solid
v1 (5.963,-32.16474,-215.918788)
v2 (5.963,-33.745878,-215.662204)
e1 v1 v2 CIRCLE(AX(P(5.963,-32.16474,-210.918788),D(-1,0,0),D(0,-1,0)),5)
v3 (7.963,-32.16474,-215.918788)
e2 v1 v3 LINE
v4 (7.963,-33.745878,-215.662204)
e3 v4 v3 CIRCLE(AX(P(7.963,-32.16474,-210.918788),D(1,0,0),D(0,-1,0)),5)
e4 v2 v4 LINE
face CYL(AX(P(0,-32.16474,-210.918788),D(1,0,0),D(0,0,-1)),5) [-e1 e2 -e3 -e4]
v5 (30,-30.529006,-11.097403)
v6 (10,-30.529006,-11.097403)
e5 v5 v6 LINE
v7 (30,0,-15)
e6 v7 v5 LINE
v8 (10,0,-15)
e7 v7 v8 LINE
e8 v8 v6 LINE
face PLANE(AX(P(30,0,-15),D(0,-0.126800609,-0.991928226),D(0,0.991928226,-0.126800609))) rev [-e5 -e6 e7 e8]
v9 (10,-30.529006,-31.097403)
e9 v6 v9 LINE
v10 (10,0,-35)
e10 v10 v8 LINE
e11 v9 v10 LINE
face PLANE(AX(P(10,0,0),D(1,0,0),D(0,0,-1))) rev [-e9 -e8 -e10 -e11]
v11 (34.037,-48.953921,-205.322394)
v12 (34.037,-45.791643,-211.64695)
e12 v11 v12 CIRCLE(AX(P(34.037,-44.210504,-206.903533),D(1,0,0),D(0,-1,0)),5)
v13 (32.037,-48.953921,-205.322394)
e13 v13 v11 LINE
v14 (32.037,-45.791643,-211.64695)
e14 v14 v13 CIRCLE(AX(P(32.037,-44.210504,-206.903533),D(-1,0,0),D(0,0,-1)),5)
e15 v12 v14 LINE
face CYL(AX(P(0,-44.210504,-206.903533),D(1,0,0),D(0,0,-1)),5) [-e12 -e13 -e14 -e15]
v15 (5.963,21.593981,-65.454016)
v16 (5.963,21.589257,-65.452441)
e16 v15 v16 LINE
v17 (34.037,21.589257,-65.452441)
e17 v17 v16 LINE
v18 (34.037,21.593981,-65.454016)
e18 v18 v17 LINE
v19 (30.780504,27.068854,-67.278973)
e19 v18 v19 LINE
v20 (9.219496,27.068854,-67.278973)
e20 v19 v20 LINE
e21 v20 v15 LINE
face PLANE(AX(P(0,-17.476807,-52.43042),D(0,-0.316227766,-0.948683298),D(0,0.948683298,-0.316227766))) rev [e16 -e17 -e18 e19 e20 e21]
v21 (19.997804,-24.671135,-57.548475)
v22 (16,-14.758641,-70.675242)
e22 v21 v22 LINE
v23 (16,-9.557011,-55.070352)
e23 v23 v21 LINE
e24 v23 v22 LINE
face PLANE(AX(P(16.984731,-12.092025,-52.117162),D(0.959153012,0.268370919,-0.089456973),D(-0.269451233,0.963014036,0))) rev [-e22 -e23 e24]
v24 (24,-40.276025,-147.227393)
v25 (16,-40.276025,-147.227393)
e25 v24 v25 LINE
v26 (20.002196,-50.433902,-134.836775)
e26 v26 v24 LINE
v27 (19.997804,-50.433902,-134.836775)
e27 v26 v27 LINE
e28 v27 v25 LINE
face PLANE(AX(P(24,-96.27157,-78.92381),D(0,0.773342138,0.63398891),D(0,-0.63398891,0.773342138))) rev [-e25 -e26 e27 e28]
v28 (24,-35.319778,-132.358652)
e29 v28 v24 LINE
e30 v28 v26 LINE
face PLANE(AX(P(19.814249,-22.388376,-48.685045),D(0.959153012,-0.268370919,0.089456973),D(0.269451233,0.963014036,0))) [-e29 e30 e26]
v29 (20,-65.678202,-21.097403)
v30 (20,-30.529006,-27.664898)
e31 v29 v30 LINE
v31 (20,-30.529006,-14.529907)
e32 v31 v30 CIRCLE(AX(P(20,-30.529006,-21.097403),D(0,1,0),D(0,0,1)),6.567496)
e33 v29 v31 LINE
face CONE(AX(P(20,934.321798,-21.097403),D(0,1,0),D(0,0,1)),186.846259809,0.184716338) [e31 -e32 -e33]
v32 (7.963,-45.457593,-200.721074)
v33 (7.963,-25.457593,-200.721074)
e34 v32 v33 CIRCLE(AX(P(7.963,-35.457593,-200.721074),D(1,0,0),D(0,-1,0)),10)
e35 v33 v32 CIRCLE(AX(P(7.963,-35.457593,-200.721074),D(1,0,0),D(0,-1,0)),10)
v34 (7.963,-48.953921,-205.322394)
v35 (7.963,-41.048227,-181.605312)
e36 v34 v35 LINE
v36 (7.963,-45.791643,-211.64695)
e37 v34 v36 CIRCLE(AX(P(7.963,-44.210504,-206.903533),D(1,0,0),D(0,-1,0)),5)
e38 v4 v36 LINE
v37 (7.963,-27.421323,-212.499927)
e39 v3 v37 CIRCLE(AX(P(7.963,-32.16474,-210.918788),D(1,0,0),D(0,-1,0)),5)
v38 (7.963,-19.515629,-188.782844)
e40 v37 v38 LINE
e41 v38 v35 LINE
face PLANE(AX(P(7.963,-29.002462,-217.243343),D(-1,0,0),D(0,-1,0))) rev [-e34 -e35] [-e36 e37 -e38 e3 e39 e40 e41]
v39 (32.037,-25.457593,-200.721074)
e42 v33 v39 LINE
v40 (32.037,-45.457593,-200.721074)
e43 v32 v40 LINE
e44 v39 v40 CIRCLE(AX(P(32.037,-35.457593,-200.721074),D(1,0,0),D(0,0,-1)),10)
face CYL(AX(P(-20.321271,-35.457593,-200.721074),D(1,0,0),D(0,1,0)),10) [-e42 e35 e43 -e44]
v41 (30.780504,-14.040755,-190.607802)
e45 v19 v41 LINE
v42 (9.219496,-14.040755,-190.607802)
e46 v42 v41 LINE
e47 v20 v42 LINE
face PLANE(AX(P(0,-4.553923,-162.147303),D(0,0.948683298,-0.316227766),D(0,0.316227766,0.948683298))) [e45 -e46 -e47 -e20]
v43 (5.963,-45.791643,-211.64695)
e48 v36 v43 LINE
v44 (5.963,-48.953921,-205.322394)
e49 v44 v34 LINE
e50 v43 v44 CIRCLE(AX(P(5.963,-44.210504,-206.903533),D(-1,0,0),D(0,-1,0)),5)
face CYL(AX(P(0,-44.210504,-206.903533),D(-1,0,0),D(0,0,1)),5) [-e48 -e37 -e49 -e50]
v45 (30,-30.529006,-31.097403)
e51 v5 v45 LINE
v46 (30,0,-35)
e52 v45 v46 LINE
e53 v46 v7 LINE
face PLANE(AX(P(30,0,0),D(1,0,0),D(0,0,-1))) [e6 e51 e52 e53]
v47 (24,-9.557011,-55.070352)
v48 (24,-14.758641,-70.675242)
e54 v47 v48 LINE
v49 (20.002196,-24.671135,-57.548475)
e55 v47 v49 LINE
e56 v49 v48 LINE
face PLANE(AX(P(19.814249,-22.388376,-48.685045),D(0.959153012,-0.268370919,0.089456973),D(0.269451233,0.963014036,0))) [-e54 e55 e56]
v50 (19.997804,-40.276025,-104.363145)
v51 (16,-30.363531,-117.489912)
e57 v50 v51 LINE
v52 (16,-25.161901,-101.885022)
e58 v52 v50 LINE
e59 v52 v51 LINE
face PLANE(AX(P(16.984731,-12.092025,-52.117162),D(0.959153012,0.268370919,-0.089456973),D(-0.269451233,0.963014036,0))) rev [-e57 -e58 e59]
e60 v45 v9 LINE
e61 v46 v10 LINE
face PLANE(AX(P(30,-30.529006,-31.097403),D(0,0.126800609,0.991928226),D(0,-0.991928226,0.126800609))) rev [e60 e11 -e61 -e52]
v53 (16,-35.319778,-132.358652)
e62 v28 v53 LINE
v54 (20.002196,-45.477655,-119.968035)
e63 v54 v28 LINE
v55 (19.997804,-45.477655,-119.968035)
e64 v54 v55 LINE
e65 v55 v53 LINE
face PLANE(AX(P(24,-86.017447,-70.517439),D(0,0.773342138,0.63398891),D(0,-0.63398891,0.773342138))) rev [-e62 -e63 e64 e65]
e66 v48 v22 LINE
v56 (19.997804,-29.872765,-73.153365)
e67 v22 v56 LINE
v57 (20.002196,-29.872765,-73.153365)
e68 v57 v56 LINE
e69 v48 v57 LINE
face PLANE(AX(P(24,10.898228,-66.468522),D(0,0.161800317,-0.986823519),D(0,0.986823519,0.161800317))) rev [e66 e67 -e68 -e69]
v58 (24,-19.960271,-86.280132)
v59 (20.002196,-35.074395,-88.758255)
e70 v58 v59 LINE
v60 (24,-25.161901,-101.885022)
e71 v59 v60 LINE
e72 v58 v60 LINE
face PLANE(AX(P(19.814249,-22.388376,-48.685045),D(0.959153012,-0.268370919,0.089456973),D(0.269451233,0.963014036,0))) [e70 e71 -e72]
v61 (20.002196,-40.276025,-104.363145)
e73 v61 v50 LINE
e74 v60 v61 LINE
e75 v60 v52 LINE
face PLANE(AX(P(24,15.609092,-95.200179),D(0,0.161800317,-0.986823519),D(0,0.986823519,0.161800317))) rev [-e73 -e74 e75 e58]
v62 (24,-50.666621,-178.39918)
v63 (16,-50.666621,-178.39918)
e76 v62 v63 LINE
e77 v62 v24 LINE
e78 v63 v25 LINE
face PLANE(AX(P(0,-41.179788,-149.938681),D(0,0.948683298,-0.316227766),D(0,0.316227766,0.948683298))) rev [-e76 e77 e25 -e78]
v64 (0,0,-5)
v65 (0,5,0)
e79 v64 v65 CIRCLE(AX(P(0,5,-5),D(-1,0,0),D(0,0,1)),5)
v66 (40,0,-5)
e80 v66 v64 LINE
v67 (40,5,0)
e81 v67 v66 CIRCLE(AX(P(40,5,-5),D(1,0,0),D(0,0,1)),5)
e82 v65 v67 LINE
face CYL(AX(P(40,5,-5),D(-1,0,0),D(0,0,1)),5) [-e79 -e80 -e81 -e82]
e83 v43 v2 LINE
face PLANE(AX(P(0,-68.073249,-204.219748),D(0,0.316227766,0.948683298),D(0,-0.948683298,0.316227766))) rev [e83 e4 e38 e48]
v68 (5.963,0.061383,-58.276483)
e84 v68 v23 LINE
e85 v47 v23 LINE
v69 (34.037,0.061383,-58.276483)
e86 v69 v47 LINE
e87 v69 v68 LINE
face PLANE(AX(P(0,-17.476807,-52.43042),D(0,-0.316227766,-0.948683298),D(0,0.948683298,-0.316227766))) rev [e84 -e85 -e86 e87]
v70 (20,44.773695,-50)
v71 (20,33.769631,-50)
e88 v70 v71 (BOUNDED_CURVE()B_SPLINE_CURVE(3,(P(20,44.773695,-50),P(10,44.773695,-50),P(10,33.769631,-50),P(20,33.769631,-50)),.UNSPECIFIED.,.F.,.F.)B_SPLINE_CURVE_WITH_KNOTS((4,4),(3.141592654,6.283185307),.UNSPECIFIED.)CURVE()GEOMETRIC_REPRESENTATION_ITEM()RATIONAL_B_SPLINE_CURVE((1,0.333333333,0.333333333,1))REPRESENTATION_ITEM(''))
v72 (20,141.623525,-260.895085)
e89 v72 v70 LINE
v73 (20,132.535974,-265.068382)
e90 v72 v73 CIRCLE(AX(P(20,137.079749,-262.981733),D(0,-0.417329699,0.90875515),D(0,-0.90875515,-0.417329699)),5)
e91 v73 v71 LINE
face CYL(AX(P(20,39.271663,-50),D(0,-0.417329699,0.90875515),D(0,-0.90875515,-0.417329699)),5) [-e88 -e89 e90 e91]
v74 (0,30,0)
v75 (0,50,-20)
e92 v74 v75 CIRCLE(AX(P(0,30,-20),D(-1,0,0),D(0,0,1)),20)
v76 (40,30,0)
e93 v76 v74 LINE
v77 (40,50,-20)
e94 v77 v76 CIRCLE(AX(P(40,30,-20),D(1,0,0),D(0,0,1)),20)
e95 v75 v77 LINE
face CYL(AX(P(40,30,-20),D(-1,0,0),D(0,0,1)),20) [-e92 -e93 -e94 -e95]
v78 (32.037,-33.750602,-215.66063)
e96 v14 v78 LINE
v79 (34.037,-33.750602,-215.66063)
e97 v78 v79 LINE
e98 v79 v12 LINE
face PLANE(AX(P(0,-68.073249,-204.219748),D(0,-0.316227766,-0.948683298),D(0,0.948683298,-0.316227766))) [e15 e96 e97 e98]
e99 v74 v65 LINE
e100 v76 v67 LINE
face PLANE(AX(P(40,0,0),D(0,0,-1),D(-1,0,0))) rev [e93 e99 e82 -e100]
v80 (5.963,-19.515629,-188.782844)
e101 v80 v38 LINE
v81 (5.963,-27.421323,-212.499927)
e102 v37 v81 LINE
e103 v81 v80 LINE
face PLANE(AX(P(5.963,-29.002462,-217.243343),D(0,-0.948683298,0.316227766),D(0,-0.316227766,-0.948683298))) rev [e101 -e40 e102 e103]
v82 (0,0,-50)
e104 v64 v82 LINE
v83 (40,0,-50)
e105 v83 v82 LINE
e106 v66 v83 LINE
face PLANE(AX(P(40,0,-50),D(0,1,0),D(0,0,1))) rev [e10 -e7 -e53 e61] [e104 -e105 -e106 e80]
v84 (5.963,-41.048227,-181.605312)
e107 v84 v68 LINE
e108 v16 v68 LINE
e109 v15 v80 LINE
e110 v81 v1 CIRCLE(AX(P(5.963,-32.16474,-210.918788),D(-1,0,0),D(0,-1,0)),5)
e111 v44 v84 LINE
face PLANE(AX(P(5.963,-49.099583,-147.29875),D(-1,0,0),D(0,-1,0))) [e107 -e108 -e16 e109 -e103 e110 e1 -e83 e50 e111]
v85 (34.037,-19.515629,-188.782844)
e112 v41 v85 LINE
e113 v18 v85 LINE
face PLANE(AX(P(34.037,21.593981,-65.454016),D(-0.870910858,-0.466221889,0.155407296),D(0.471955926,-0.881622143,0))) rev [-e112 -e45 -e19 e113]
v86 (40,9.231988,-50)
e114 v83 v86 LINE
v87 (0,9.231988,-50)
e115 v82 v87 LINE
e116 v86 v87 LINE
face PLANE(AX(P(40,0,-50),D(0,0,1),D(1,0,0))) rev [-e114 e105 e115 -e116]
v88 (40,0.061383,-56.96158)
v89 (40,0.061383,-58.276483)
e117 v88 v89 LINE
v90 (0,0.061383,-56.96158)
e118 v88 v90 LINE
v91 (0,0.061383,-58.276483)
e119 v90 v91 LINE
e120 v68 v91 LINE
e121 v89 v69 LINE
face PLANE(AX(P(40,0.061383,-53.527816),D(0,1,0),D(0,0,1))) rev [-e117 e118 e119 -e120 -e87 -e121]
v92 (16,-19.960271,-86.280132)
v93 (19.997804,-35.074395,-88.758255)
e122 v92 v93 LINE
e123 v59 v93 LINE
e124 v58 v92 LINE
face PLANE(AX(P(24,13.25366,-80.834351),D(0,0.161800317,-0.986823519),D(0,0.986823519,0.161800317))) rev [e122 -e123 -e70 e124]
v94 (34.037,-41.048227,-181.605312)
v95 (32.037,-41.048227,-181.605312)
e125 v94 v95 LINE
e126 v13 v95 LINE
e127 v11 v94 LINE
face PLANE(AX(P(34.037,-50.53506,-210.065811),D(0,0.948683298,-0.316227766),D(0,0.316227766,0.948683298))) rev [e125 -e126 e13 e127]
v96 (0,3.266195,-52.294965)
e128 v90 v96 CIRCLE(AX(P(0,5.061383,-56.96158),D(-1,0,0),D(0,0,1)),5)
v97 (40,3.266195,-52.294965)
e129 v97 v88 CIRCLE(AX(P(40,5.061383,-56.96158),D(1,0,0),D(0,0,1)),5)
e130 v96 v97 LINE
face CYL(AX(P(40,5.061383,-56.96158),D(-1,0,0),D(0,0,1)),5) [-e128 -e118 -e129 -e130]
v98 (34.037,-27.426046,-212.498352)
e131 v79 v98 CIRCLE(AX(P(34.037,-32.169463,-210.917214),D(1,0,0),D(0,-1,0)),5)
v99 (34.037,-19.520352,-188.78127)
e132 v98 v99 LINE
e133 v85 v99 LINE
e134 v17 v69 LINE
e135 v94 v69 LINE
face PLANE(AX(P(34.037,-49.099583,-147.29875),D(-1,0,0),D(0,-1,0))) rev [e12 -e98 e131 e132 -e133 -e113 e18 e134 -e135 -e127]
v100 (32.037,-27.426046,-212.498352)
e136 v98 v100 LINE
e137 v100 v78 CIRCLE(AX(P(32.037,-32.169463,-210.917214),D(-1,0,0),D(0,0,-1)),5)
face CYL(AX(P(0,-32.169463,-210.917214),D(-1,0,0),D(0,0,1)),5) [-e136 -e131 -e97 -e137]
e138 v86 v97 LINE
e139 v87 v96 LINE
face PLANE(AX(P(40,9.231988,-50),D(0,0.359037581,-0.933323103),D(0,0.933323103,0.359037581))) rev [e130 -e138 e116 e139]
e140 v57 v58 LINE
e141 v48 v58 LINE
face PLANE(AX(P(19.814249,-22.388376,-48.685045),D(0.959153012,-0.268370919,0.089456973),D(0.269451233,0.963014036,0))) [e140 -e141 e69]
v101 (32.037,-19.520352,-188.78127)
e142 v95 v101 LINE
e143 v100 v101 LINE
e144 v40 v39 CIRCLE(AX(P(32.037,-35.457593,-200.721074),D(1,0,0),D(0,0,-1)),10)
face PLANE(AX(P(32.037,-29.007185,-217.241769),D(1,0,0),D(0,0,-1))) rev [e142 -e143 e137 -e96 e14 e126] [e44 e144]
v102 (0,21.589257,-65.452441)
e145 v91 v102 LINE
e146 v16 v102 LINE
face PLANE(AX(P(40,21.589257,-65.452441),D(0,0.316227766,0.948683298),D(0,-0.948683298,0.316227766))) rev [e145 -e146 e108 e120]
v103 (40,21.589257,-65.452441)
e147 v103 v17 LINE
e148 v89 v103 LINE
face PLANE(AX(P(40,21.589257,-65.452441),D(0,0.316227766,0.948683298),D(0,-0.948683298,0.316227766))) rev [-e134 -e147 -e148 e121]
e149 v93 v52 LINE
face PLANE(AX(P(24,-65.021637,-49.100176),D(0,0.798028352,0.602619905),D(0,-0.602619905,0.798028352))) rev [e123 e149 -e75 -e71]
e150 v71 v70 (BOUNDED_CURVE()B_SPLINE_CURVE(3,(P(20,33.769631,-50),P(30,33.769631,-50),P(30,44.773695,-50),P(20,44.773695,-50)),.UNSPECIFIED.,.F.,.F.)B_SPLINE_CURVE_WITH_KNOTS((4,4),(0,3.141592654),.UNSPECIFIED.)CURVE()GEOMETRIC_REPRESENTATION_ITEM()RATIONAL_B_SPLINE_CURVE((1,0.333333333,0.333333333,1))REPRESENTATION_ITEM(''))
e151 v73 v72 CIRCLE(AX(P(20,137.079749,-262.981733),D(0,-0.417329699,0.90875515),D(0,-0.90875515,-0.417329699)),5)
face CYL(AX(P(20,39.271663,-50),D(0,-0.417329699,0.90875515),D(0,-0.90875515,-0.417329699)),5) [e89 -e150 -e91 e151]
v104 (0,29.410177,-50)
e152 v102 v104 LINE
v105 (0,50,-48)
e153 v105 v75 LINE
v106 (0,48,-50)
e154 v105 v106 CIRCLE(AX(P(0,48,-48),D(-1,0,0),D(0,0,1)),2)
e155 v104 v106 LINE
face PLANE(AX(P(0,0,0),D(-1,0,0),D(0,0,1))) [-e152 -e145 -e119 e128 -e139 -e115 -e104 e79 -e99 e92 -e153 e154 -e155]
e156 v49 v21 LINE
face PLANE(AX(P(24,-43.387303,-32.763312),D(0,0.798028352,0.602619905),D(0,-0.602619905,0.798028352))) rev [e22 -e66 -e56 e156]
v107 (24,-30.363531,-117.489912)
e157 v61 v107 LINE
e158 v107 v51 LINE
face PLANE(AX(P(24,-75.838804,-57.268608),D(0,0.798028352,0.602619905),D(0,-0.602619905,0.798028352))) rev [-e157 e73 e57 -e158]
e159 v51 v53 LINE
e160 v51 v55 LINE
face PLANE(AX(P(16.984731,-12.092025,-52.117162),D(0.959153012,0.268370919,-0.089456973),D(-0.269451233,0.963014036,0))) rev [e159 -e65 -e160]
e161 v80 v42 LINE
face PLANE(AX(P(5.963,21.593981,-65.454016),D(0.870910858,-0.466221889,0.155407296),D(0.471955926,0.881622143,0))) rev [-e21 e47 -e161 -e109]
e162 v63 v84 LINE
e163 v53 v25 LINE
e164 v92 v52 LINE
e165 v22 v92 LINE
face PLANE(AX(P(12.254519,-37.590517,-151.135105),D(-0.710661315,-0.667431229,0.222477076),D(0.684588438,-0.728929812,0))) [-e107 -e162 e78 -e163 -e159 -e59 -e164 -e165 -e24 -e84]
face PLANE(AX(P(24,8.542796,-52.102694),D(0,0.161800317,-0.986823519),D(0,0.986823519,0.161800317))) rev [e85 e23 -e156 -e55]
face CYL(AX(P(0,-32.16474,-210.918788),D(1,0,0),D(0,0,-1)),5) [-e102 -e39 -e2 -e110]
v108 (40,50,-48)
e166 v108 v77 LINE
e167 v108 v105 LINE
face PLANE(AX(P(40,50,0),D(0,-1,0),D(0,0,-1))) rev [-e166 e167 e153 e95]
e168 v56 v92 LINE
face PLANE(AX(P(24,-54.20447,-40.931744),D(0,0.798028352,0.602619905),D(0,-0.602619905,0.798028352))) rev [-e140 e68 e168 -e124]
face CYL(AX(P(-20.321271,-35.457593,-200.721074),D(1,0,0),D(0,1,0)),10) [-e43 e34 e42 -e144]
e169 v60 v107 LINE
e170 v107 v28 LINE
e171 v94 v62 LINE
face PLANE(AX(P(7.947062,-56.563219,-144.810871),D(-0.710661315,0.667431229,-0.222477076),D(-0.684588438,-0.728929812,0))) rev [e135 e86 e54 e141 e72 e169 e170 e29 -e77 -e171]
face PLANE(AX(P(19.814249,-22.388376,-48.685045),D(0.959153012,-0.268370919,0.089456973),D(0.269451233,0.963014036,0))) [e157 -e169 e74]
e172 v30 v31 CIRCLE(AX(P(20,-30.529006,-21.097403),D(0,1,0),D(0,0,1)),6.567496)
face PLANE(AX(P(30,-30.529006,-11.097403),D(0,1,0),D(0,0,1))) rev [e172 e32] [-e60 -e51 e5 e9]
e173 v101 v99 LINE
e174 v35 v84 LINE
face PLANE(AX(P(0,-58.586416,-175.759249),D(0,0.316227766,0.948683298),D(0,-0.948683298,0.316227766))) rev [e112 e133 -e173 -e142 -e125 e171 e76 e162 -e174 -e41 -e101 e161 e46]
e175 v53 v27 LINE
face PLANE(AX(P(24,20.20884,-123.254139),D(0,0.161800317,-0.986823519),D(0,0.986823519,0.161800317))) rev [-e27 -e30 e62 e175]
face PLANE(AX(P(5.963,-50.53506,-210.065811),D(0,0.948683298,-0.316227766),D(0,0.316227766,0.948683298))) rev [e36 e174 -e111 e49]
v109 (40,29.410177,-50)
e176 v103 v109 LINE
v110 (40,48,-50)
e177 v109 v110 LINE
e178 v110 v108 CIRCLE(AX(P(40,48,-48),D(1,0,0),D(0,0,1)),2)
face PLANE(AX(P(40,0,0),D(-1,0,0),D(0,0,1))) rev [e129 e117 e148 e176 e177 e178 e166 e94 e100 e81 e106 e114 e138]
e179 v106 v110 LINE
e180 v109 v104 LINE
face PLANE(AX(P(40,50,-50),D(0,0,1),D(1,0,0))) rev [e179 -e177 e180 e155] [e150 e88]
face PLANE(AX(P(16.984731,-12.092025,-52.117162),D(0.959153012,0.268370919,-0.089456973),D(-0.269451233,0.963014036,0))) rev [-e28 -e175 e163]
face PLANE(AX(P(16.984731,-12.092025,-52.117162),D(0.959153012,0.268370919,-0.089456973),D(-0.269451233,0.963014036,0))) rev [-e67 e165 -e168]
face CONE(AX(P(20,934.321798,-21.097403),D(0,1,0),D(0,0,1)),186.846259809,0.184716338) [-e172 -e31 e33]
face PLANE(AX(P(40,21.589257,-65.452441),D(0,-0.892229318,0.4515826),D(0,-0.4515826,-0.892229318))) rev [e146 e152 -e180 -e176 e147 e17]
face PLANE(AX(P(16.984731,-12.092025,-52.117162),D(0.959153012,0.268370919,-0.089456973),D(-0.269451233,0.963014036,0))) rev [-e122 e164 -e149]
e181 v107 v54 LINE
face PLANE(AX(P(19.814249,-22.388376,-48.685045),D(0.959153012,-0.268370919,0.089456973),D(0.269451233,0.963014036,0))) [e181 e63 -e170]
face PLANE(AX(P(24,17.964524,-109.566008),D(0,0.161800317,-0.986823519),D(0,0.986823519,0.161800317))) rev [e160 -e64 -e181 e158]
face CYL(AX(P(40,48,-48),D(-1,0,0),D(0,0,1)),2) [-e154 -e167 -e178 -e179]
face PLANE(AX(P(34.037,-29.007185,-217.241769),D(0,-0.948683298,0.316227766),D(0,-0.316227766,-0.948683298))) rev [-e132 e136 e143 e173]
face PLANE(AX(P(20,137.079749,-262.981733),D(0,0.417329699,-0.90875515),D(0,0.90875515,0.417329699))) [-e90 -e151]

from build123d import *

# Parameters (mm, degrees)
BOSS_EXTRUDE1_DEPTH  = 40
FILLET1_R            = 20
FILLET2_R            = 5
BOSS_EXTRUDE2_DEPTH  = 10
FILLET3_R            = 5
FILLET4_R            = 2
BOSS_EXTRUDE6_DEPTH  = 100
BOSS_EXTRUDE8_DEPTH  = 4
CUT_EXTRUDE5_DEPTH   = 102
BOSS_EXTRUDE14_DEPTH = 30
CUT_EXTRUDE4_DEPTH   = 100
SKETCH25_W           = 2
SKETCH25_H           = 22.692372085
SKETCH25_H_2         = 22.697350811
BOSS_EXTRUDE15_DEPTH = 30
SKETCH26_R           = 10
BOSS_EXTRUDE16_DEPTH = 26.073999752
FILLET5_R            = 5


with BuildPart() as part:
    # Sketch2 → Boss-Extrude1 (new body)
    with BuildSketch(Plane(origin=(0, 0, 0), x_dir=(0, 0, -1), z_dir=(1, 0, 0))):
        Polygon((0, 0), (0, 50), (50, 50), (50, 29.410176709), (65.452441178, 21.589257338), (58.276483048, 0.061382948), (53.5278156, 0.061382948), (50, 9.231987855), (50, 0), align=None)
    extrude(amount=BOSS_EXTRUDE1_DEPTH)

    # Fillet1
    fillet1_edges = [part.edges().sort_by_distance(p)[0] for p in [
        (20, 50, 0),
    ]]
    fillet(fillet1_edges, radius=FILLET1_R)

    # Fillet2
    fillet2_edges = [part.edges().sort_by_distance(p)[0] for p in [
        (20, 0, 0),
    ]]
    fillet(fillet2_edges, radius=FILLET2_R)

    # Sketch4 → Boss-Extrude2 (add, symmetric)
    with BuildSketch(Plane(origin=(20, 0, 0), x_dir=(0, 0, -1), z_dir=(1, 0, 0))):
        Polygon((15, 0), (11.097402588, -30.529005874), (31.097402588, -30.529005874), (35, 0), align=None)
    extrude(amount=BOSS_EXTRUDE2_DEPTH, both=True)

    # Sketch5 → Revolve1 (revolve)
    with BuildSketch(Plane(origin=(20, 0, 0), x_dir=(0, 0, -1), z_dir=(1, 0, 0)), mode=Mode.PRIVATE) as revolve1_sk:
        Polygon((21.097402588, -30.529005874), (27.664898482, -30.529005874), (21.097402588, -65.678202337), align=None)
    revolve(revolve1_sk.sketch.rotate(Axis((20, -30.529005874, -21.097402588), (0, -1, 0)), 180), axis=Axis((20, -30.529005874, -21.097402588), (0, -1, 0)))

    # Fillet3
    fillet3_edges = [part.edges().sort_by_distance(p)[0] for p in [
        (20, 0.061382948, -53.5278156),
    ]]
    fillet(fillet3_edges, radius=FILLET3_R)

    # Fillet4
    fillet4_edges = [part.edges().sort_by_distance(p)[0] for p in [
        (20, 50, -50),
    ]]
    fillet(fillet4_edges, radius=FILLET4_R)

    # Sketch7 → Boss-Extrude6 (add)
    with BuildSketch(Plane(origin=(0, -17.47680662, -52.430419859), x_dir=(-1, 0, 0), z_dir=(0, -0.3162277660168374, -0.9486832980505141))):
        Polygon((-5.963000124, 18.486875023), (-16, 8.348197136), (-24, 8.348197136), (-34.036999876, 18.486875023), (-34.036999876, 46.955249244), (-5.963000124, 46.955249244), align=None)
    extrude(amount=BOSS_EXTRUDE6_DEPTH)

    # Sketch10 → Boss-Extrude8 (add, symmetric)
    with BuildSketch(Plane(origin=(20, 0, 0), x_dir=(0, 0, -1), z_dir=(1, 0, 0))):
        Polygon((147.227393234, -40.276025309), (132.358652474, -35.319778389), (134.836775442, -50.433902239), align=None)
        Polygon((132.358652474, -35.319778389), (117.489911715, -30.363531469), (119.968034683, -45.477655319), align=None)
        Polygon((117.489911715, -30.363531469), (101.885021683, -25.161901459), (104.363144652, -40.276025309), align=None)
        Polygon((101.885021683, -25.161901459), (86.280131652, -19.960271448), (88.75825462, -35.074395299), align=None)
        Polygon((86.280131652, -19.960271448), (70.675241621, -14.758641438), (73.153364589, -29.872765288), align=None)
        Polygon((70.675241621, -14.758641438), (55.07035159, -9.557011428), (57.548474558, -24.671135278), align=None)
    extrude(amount=BOSS_EXTRUDE8_DEPTH, both=True)

    # Sketch23 → Cut-Extrude5 (cut)
    with BuildSketch(Plane(origin=(0, -49.099583221, -147.298749664), x_dir=(-1, 0, 0), z_dir=(0, -0.3162277660168373, -0.948683298050514))):
        Polygon((-16, -5.206668435), (-16, 8.348197136), (-20, -5.214113496), align=None)
        Polygon((-24, -5.206668435), (-24, 8.348197136), (-20, -5.214113496), align=None)
    extrude(amount=-CUT_EXTRUDE5_DEPTH, mode=Mode.SUBTRACT)

    # Sketch24 → Boss-Extrude14 (add)
    with BuildSketch(Plane(origin=(0, -49.099583221, -147.298749664), x_dir=(-1, 0, 0), z_dir=(0, -0.3162277660168373, -0.948683298050514))):
        Polygon((-5.963000124, 18.486875023), (-5.963000124, 46.955249244), (-34.036999876, 46.955249244), (-34.036999876, 18.486875023), (-24, 8.348197136), (-16, 8.348197136), align=None)
    extrude(amount=BOSS_EXTRUDE14_DEPTH)

    # Sketch20 → Cut-Extrude4 (cut, symmetric)
    with BuildSketch(Plane(origin=(0, -49.099583221, -147.298749664), x_dir=(-1, 0, 0), z_dir=(0, -0.3162277660168373, -0.948683298050514))):
        Polygon((-34.036999876, 41.184225834), (-30.780503979, 46.955249244), (-34.036999876, 46.955249244), align=None)
        Polygon((-5.963000124, 41.184225834), (-9.219496021, 46.955249244), (-5.963000124, 46.955249244), align=None)
    extrude(amount=CUT_EXTRUDE4_DEPTH, both=True, mode=Mode.SUBTRACT)

    # Sketch25 → Boss-Extrude15 (add)
    with BuildSketch(Plane(origin=(0, -58.586416202, -175.759248606), x_dir=(-1, 0, 0), z_dir=(0, -0.31622776601683655, -0.9486832980505142))):
        with Locations((-33.036999876, 29.833061066)):
            Rectangle(SKETCH25_W, SKETCH25_H)
        with Locations((-6.963000124, 29.835550428)):
            Rectangle(SKETCH25_W, SKETCH25_H_2)
    extrude(amount=BOSS_EXTRUDE15_DEPTH)

    # Sketch26 → Boss-Extrude16 (add)
    with BuildSketch(Plane(origin=(34.036999876, 0, 0), x_dir=(0, 0, -1), z_dir=(1, 0, 0))):
        with Locations((200.721074436, -35.457593279)):
            Circle(SKETCH26_R)
    extrude(amount=-BOSS_EXTRUDE16_DEPTH)

    # Fillet5
    fillet5_edges = [part.edges().sort_by_distance(p)[0] for p in [
        (33.036999876, -50.535059615, -210.065810737),
        (33.036999876, -29.007185225, -217.241768866),
        (6.963000124, -29.00246199, -217.243343278),
        (6.963000124, -50.535059615, -210.065810737),
    ]]
    fillet(fillet5_edges, radius=FILLET5_R)

    # Sketch28 → Revolve3 (revolve)
    with BuildSketch(Plane(origin=(20, 0, 0), x_dir=(0, 0, -1), z_dir=(1, 0, 0))):
        Polygon((50, 33.769630528), (50, 39.271662622), (262.981733141, 137.079749362), (265.068381635, 132.535973612), align=None)
    revolve(axis=Axis((20, 39.271662622, -50), (0, 0.4173296987488473, -0.9087551499398484)))


solid = part.part
